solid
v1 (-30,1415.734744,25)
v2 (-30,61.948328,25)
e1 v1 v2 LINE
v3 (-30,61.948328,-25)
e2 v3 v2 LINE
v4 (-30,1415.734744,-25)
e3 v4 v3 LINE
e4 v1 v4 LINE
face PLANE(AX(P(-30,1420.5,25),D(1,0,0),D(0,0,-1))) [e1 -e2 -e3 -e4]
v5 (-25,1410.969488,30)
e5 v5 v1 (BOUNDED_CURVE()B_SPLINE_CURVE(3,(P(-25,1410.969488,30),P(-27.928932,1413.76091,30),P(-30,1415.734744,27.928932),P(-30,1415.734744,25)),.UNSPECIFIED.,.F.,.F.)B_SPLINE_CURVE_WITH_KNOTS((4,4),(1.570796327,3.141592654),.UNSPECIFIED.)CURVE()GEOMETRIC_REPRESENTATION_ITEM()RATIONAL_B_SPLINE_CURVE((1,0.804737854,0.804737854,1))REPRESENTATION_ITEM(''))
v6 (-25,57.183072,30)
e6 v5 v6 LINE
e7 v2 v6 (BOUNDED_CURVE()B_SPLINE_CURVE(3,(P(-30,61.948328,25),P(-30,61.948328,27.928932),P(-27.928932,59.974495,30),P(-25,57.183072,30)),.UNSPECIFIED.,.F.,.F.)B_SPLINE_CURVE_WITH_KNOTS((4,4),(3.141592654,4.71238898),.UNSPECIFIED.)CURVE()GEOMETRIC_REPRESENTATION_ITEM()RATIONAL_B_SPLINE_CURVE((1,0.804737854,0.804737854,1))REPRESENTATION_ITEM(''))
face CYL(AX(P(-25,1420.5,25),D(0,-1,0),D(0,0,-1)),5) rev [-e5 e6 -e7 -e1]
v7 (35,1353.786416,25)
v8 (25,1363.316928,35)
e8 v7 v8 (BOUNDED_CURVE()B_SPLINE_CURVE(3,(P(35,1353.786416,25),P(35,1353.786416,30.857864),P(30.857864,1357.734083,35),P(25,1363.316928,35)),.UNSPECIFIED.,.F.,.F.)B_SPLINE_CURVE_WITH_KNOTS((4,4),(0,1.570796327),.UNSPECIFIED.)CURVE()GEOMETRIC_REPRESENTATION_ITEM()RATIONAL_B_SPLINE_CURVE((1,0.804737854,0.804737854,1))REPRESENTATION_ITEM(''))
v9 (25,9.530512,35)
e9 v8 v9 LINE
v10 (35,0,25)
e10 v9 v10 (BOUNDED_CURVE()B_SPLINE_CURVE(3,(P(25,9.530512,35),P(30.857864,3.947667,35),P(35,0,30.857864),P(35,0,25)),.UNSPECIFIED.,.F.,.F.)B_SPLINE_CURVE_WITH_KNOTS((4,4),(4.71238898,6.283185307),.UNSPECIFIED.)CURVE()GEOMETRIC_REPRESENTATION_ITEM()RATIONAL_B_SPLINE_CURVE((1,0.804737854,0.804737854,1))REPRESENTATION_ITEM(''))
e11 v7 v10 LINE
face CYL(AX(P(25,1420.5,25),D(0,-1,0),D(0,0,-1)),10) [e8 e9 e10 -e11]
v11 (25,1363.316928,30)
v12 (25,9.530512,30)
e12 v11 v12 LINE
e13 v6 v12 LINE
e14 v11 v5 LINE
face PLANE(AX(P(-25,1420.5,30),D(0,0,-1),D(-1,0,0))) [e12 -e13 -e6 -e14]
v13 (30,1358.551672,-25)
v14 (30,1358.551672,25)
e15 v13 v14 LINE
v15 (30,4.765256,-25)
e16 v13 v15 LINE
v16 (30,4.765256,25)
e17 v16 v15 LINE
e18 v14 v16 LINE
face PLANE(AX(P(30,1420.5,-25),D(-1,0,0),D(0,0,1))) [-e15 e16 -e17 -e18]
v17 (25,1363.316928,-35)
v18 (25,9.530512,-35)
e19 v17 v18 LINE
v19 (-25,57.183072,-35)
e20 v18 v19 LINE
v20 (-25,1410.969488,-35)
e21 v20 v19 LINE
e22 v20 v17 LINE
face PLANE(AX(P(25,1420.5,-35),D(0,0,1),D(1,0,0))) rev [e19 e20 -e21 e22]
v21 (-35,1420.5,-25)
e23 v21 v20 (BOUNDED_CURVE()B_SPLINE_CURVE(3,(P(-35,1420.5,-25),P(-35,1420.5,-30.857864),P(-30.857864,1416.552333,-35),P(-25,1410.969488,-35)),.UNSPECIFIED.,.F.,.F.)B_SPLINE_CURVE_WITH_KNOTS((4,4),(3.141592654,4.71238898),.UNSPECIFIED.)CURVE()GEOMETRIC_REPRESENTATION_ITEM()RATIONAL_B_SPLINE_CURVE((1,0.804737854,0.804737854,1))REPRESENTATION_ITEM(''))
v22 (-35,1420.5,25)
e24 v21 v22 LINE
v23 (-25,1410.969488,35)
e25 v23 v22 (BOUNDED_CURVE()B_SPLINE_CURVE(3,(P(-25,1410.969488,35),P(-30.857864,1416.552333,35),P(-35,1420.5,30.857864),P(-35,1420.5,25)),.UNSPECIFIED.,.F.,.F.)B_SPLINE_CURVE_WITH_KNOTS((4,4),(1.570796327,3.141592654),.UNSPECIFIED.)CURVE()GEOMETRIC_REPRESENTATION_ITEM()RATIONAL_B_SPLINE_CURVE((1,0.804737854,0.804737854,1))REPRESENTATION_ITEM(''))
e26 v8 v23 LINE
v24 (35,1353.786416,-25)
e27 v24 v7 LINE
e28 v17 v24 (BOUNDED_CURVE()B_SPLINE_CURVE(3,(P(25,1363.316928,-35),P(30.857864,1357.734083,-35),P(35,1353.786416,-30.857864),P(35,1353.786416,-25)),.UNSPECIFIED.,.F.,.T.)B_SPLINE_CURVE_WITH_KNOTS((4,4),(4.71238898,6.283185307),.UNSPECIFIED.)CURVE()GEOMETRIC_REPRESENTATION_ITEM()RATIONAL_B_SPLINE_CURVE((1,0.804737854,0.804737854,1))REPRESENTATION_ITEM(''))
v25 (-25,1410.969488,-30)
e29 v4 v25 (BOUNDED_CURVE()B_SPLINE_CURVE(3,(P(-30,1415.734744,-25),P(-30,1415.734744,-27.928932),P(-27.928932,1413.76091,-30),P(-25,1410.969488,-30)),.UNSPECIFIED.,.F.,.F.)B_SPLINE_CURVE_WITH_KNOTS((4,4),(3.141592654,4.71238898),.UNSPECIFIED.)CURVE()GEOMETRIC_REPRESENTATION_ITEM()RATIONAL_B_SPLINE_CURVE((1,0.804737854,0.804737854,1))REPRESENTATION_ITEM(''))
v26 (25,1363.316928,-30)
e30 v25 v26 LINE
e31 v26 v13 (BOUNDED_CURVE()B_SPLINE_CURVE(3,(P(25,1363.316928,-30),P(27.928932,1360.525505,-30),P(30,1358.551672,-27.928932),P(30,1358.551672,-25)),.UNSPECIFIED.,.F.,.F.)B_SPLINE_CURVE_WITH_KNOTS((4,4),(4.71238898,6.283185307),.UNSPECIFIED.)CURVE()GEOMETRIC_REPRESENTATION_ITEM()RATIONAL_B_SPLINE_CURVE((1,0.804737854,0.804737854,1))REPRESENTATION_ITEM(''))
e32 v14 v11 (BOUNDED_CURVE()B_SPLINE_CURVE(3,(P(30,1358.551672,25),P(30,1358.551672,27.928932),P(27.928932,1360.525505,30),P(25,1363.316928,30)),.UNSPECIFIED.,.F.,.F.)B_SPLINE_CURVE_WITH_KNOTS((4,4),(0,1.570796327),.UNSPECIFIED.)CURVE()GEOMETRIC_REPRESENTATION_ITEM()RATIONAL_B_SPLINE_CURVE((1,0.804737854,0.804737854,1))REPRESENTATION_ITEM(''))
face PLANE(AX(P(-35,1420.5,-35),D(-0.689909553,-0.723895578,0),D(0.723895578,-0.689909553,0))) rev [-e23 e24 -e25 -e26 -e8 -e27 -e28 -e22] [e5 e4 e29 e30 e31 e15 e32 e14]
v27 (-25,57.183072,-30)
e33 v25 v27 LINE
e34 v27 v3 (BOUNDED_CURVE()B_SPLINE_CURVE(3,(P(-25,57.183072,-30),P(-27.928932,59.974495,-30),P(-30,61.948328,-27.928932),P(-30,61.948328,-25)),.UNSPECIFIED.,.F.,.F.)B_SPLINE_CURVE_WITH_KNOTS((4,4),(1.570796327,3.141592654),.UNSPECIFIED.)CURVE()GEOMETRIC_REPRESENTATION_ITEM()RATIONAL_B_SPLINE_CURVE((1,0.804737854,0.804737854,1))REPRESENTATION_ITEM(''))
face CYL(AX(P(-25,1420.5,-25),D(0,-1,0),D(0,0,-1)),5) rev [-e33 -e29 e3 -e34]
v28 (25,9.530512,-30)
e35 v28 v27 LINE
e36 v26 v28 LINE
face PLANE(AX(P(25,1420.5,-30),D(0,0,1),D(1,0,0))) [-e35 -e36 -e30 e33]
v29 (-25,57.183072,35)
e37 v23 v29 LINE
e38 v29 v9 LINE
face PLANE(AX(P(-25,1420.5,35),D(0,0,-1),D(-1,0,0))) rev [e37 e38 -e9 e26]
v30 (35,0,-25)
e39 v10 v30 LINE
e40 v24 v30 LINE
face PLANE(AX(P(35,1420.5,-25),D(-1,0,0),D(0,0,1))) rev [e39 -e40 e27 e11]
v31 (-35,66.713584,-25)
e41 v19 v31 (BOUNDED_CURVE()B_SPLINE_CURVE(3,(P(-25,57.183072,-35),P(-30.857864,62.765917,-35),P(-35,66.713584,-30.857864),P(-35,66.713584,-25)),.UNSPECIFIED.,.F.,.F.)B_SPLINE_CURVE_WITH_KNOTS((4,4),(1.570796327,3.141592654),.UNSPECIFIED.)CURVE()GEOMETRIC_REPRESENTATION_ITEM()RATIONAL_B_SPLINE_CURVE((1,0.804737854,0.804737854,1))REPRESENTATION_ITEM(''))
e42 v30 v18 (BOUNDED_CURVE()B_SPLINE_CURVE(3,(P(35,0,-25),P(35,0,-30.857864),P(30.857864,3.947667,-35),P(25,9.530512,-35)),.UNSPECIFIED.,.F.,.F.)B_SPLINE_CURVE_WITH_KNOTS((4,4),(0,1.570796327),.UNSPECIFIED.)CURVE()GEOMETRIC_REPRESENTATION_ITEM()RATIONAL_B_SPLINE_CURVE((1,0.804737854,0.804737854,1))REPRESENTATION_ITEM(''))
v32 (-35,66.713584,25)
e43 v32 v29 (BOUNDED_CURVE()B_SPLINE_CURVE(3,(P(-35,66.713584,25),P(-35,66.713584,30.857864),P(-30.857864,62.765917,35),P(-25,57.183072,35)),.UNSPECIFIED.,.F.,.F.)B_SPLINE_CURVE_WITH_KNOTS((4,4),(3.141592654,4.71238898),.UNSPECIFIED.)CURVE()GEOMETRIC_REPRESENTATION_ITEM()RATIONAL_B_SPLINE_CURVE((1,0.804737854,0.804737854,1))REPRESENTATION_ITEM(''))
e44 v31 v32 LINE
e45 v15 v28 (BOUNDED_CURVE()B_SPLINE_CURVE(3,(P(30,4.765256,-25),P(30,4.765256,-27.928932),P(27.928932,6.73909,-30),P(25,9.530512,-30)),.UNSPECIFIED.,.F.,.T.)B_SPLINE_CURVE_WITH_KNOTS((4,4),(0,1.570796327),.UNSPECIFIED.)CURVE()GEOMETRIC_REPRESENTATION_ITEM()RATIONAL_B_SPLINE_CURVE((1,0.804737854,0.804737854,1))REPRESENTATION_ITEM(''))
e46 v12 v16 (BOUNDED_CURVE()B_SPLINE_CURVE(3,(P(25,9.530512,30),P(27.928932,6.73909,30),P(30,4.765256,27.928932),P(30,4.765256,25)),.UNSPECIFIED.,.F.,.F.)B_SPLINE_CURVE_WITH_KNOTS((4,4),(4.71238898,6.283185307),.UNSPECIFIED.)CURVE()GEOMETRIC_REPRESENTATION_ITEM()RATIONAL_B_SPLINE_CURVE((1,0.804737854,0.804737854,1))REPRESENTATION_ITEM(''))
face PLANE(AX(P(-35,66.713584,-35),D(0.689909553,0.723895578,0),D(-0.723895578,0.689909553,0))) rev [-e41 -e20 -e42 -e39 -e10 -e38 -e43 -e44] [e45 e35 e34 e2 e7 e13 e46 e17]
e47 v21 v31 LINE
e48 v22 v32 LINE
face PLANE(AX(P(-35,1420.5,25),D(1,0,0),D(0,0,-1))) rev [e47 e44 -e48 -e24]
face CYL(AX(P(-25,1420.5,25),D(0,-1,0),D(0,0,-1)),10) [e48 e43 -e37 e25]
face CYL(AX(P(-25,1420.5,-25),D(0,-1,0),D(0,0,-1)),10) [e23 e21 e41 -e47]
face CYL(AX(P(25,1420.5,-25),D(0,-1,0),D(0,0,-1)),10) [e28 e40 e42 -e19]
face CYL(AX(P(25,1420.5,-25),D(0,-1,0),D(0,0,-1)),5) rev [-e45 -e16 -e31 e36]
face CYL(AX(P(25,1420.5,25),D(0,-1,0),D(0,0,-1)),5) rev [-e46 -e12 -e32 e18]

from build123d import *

# Parameters (mm, degrees)
F_19_WELDMEMBERFEAT_4_MORE_IN_5_FILES_DEPTH = 1420.5
CUT_EXTRUDE1_DEPTH                          = 1423.654297431
CUT_EXTRUDE1_DEPTH_BACK                     = 1423.654297431


with BuildPart() as part:
    # Sketch1 → 19 (WeldMemberFeat) (+4 more in 5 files) Cold-formed hollow square steel (GB/T 6728-2002) 70×70×5(1) (new body)
    with BuildSketch(Plane(origin=(0, 0, 0), x_dir=(-1, 0, 0), z_dir=(0, 1, 0))):
        with BuildLine():
            Line((-25, -35), (25, -35))
            ThreePointArc((25, -35), (32.071067812, -32.071067812), (35, -25))
            Line((35, -25), (35, 25))
            ThreePointArc((35, 25), (32.071067812, 32.071067812), (25, 35))
            Line((25, 35), (-25, 35))
            ThreePointArc((-25, 35), (-32.071067812, 32.071067812), (-35, 25))
            Line((-35, 25), (-35, -25))
            ThreePointArc((-35, -25), (-32.071067812, -32.071067812), (-25, -35))
        make_face()
        with BuildLine():
            Line((-25, -30), (25, -30))
            ThreePointArc((25, -30), (28.535533906, -28.535533906), (30, -25))
            Line((30, -25), (30, 25))
            ThreePointArc((30, 25), (28.535533906, 28.535533906), (25, 30))
            Line((25, 30), (-25, 30))
            ThreePointArc((-25, 30), (-28.535533906, 28.535533906), (-30, 25))
            Line((-30, 25), (-30, -25))
            ThreePointArc((-30, -25), (-28.535533906, -28.535533906), (-25, -30))
        make_face(mode=Mode.SUBTRACT)
    extrude(amount=F_19_WELDMEMBERFEAT_4_MORE_IN_5_FILES_DEPTH)

    # Sketch2 → Cut-Extrude1 (cut, two sides: drawn at the far end of the back side and taken through both)
    with BuildSketch(Plane.XY.offset(35).offset(-CUT_EXTRUDE1_DEPTH_BACK)):
        Polygon((-35, 66.713584391), (35, 0), (-35, 0), align=None)
        Polygon((-35, 1420.5), (35, 1353.786415609), (35, 1420.5), align=None)
    extrude(amount=CUT_EXTRUDE1_DEPTH + CUT_EXTRUDE1_DEPTH_BACK, mode=Mode.SUBTRACT)


solid = part.part
